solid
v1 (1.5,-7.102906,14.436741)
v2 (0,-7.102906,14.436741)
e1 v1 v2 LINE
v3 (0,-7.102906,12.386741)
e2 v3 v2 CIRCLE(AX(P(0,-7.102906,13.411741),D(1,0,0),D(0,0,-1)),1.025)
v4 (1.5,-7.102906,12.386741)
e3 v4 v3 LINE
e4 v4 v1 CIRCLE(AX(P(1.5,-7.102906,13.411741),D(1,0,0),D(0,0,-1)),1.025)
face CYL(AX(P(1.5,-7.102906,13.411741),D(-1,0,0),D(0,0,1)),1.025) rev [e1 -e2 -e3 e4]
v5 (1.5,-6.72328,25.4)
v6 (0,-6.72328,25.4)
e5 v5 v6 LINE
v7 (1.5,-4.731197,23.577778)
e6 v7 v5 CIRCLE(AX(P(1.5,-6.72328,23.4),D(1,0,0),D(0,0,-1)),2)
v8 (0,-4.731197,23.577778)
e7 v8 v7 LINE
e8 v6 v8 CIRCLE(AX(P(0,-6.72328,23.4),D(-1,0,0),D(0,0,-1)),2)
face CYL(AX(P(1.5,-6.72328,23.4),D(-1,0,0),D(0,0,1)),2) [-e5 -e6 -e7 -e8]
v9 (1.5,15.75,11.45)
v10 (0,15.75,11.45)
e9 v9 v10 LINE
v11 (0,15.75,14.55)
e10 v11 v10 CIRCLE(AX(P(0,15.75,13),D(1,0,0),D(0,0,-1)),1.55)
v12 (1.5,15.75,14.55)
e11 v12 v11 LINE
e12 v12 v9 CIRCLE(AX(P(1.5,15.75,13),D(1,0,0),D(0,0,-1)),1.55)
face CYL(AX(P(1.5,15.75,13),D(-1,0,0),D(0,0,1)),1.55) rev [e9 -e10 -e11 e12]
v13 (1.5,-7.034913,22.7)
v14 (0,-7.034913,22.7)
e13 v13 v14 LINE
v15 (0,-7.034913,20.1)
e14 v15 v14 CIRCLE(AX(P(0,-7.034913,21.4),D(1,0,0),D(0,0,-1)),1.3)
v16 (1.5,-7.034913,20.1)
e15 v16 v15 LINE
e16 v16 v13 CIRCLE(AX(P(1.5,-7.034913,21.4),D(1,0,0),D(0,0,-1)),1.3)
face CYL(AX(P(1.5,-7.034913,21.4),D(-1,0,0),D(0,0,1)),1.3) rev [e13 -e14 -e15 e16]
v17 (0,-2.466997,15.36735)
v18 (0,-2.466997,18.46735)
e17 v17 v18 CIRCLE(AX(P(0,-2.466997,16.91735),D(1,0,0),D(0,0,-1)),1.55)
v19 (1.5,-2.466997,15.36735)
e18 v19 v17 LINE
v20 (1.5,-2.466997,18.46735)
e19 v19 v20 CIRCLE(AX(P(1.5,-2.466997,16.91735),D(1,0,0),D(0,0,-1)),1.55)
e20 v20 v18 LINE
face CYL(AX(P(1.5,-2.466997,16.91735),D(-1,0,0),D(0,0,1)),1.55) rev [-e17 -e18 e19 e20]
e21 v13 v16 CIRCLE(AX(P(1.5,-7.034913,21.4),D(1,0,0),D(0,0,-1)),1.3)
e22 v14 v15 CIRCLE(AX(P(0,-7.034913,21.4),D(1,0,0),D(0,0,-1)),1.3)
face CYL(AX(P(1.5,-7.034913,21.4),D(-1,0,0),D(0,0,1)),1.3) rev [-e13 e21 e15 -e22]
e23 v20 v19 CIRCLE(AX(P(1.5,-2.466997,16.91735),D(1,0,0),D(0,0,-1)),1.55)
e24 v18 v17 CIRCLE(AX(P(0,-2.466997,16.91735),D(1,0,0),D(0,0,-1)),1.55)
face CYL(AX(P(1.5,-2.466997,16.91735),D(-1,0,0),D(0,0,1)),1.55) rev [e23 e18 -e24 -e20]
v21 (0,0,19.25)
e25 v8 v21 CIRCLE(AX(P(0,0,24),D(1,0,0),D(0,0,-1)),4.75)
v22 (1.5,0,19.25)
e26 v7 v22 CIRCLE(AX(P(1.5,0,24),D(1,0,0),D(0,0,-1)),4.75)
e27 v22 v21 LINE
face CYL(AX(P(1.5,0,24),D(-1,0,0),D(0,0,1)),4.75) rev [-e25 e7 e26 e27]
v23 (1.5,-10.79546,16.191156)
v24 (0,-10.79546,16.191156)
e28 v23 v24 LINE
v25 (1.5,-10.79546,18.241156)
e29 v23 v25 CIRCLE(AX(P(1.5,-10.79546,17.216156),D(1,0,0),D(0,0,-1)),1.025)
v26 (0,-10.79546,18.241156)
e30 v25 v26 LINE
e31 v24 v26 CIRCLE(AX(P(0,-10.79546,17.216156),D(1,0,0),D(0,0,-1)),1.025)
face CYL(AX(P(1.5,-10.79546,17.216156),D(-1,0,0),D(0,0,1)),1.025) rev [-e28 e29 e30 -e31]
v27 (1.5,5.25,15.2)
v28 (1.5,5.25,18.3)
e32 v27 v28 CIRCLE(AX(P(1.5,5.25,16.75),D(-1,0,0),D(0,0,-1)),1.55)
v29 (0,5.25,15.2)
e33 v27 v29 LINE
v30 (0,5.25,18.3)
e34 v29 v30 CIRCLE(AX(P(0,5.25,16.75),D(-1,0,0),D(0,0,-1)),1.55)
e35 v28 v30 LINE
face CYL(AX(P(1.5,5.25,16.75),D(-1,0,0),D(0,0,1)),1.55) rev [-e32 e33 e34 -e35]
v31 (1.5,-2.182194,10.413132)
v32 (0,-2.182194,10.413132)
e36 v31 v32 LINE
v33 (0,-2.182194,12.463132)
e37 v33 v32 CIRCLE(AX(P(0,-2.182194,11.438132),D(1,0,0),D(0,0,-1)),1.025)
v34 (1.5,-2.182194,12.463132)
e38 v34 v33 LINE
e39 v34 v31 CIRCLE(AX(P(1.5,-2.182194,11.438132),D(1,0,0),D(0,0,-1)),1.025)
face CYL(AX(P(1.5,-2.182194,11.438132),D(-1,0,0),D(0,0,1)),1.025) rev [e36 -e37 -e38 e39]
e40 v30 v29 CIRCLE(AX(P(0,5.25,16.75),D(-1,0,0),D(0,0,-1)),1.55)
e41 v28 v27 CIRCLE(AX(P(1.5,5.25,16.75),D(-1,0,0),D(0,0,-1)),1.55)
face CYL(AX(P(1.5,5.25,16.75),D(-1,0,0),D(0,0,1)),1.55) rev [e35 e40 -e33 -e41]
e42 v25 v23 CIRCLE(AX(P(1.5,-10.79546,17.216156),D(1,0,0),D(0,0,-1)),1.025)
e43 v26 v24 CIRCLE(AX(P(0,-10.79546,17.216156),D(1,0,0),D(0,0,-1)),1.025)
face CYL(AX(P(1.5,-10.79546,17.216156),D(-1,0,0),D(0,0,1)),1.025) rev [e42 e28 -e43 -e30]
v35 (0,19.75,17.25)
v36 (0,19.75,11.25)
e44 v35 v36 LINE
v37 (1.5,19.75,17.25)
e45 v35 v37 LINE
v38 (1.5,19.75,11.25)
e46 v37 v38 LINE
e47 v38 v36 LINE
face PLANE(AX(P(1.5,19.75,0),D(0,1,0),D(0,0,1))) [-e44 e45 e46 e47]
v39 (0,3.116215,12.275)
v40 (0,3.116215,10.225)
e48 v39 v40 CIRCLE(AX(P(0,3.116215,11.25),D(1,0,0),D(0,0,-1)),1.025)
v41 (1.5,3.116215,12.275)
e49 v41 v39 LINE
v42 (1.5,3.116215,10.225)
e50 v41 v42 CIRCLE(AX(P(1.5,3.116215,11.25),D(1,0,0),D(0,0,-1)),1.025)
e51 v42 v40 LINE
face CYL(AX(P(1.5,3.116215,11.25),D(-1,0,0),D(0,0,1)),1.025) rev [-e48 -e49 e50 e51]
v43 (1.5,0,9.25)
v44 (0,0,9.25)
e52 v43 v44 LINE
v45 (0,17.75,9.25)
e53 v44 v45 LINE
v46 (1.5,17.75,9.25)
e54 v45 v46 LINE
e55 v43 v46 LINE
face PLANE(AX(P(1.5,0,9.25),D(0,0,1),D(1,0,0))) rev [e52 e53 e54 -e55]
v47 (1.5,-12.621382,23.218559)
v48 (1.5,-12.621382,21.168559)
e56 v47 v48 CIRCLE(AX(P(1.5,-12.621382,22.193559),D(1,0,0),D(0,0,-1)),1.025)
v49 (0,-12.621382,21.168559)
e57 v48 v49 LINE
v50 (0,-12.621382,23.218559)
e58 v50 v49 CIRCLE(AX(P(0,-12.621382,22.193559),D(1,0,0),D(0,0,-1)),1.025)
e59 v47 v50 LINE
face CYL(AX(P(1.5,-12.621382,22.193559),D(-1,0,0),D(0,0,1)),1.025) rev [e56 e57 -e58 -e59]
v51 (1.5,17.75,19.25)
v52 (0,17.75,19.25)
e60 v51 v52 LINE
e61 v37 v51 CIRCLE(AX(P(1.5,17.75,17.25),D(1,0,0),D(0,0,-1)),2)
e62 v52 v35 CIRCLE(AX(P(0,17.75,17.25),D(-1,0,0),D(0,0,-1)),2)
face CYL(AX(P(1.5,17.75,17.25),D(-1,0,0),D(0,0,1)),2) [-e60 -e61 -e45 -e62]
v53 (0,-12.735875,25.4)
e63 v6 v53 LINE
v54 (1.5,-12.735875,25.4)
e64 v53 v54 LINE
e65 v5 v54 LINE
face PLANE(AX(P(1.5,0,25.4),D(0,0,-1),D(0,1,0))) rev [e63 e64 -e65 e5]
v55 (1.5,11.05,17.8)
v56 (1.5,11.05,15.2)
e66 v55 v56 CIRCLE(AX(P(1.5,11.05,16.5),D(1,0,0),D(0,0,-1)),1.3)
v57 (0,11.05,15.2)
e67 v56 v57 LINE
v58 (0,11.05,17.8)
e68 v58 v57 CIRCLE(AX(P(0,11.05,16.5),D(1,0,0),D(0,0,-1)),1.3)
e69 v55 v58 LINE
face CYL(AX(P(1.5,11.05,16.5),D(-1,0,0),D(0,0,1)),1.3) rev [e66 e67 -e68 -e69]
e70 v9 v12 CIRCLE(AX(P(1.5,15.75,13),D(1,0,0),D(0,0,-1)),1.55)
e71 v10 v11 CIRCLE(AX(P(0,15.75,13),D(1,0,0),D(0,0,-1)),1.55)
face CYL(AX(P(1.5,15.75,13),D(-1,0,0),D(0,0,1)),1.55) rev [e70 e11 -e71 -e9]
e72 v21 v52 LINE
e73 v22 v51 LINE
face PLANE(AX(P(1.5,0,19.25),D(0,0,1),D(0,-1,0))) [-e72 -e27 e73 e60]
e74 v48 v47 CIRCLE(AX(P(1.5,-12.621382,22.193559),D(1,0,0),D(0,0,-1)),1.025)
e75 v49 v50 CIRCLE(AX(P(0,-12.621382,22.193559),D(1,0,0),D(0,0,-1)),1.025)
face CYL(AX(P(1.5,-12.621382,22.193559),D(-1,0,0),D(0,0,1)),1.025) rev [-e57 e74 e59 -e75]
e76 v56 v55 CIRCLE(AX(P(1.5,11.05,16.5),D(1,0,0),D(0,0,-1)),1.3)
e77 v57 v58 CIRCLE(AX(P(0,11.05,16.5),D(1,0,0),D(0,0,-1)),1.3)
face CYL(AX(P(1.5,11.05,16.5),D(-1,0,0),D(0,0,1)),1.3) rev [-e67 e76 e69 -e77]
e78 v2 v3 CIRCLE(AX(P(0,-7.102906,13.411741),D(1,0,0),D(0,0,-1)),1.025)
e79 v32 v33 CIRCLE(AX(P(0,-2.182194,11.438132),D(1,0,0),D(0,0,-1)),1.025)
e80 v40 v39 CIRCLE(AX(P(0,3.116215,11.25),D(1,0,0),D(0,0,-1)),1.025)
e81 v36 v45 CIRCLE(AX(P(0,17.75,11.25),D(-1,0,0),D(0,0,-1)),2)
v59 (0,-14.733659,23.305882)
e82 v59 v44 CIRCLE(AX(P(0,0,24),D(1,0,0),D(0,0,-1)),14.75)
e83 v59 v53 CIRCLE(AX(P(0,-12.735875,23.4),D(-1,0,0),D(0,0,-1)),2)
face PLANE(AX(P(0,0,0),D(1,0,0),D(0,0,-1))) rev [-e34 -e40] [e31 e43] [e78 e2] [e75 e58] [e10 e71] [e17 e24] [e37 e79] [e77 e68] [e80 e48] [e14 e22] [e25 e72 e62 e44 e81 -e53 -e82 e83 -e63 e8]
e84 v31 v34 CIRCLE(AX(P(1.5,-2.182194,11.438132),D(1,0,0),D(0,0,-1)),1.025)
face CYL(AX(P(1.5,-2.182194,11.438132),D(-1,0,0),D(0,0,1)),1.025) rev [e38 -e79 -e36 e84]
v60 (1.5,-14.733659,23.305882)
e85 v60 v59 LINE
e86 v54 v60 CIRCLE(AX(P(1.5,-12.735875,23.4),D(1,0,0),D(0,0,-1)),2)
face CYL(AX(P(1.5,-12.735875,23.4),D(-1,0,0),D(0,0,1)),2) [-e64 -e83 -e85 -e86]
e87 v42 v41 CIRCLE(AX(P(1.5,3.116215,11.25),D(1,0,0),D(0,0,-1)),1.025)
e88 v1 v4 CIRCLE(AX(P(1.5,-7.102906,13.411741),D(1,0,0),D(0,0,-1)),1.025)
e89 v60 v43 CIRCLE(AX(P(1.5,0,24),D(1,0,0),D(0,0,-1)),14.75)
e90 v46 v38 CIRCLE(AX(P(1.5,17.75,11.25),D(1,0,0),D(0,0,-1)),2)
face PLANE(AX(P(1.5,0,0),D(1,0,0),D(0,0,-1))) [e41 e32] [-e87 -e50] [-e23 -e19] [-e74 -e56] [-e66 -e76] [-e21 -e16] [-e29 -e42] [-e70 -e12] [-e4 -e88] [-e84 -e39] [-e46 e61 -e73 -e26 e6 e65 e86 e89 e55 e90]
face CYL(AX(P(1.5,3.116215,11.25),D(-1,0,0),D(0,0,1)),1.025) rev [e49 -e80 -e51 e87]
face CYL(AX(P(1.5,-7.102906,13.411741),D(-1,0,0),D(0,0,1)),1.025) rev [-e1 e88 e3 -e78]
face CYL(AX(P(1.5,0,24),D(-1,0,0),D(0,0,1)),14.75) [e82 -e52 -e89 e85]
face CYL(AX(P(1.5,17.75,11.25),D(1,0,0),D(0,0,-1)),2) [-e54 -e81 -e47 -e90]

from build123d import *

# Parameters (mm, degrees)
SKETCH_1_R      = 1.025
SKETCH_1_R_2    = 1.3
SKETCH_1_R_3    = 1.55
EXTRUDE_1_DEPTH = 1.5
FILLET_R2_1_R   = 2


with BuildPart() as part:
    # 草图1 → 凸台-拉伸1 (new body)
    with BuildSketch(Plane(origin=(0, 0, 0), x_dir=(0, 0, -1), z_dir=(1, 0, 0))):
        with BuildLine():
            Line((-9.25, 0), (-9.25, 19.75))
            Line((-9.25, 19.75), (-19.25, 19.75))
            Line((-19.25, 19.75), (-19.25, 0))
            ThreePointArc((-19.25, 0), (-20.641242789, -3.358757211), (-24, -4.75))
            Line((-24, -4.75), (-25.4, -4.75))
            Line((-25.4, -4.75), (-25.4, -14.75))
            Line((-25.4, -14.75), (-24, -14.75))
            ThreePointArc((-24, -14.75), (-13.570174977, -10.429825023), (-9.25, 0))
        make_face()
        with Locations((-11.438131953, -2.182194118)):
            Circle(SKETCH_1_R, mode=Mode.SUBTRACT)
        with Locations((-13.411740816, -7.102905565)):
            Circle(SKETCH_1_R, mode=Mode.SUBTRACT)
        with Locations((-17.216155884, -10.795460111)):
            Circle(SKETCH_1_R, mode=Mode.SUBTRACT)
        with Locations((-22.193559229, -12.621381531)):
            Circle(SKETCH_1_R, mode=Mode.SUBTRACT)
        with Locations((-11.25, 3.116215025)):
            Circle(SKETCH_1_R, mode=Mode.SUBTRACT)
        with Locations((-21.4, -7.034912935)):
            Circle(SKETCH_1_R_2, mode=Mode.SUBTRACT)
        with Locations((-16.917350474, -2.466997302)):
            Circle(SKETCH_1_R_3, mode=Mode.SUBTRACT)
        with Locations((-16.75, 5.25)):
            Circle(SKETCH_1_R_3, mode=Mode.SUBTRACT)
        with Locations((-13, 15.75)):
            Circle(SKETCH_1_R_3, mode=Mode.SUBTRACT)
        with Locations((-16.5, 11.05)):
            Circle(SKETCH_1_R_2, mode=Mode.SUBTRACT)
    extrude(amount=EXTRUDE_1_DEPTH)

    # R2 圆角1
    fillet_r2_1_edges = [part.edges().sort_by_distance(p)[0] for p in [
        (0.75, 19.75, 19.25),
        (0.75, 19.75, 9.25),
        (0.75, -4.75, 25.4),
        (0.75, -14.75, 25.4),
    ]]
    fillet(fillet_r2_1_edges, radius=FILLET_R2_1_R)


solid = part.part
